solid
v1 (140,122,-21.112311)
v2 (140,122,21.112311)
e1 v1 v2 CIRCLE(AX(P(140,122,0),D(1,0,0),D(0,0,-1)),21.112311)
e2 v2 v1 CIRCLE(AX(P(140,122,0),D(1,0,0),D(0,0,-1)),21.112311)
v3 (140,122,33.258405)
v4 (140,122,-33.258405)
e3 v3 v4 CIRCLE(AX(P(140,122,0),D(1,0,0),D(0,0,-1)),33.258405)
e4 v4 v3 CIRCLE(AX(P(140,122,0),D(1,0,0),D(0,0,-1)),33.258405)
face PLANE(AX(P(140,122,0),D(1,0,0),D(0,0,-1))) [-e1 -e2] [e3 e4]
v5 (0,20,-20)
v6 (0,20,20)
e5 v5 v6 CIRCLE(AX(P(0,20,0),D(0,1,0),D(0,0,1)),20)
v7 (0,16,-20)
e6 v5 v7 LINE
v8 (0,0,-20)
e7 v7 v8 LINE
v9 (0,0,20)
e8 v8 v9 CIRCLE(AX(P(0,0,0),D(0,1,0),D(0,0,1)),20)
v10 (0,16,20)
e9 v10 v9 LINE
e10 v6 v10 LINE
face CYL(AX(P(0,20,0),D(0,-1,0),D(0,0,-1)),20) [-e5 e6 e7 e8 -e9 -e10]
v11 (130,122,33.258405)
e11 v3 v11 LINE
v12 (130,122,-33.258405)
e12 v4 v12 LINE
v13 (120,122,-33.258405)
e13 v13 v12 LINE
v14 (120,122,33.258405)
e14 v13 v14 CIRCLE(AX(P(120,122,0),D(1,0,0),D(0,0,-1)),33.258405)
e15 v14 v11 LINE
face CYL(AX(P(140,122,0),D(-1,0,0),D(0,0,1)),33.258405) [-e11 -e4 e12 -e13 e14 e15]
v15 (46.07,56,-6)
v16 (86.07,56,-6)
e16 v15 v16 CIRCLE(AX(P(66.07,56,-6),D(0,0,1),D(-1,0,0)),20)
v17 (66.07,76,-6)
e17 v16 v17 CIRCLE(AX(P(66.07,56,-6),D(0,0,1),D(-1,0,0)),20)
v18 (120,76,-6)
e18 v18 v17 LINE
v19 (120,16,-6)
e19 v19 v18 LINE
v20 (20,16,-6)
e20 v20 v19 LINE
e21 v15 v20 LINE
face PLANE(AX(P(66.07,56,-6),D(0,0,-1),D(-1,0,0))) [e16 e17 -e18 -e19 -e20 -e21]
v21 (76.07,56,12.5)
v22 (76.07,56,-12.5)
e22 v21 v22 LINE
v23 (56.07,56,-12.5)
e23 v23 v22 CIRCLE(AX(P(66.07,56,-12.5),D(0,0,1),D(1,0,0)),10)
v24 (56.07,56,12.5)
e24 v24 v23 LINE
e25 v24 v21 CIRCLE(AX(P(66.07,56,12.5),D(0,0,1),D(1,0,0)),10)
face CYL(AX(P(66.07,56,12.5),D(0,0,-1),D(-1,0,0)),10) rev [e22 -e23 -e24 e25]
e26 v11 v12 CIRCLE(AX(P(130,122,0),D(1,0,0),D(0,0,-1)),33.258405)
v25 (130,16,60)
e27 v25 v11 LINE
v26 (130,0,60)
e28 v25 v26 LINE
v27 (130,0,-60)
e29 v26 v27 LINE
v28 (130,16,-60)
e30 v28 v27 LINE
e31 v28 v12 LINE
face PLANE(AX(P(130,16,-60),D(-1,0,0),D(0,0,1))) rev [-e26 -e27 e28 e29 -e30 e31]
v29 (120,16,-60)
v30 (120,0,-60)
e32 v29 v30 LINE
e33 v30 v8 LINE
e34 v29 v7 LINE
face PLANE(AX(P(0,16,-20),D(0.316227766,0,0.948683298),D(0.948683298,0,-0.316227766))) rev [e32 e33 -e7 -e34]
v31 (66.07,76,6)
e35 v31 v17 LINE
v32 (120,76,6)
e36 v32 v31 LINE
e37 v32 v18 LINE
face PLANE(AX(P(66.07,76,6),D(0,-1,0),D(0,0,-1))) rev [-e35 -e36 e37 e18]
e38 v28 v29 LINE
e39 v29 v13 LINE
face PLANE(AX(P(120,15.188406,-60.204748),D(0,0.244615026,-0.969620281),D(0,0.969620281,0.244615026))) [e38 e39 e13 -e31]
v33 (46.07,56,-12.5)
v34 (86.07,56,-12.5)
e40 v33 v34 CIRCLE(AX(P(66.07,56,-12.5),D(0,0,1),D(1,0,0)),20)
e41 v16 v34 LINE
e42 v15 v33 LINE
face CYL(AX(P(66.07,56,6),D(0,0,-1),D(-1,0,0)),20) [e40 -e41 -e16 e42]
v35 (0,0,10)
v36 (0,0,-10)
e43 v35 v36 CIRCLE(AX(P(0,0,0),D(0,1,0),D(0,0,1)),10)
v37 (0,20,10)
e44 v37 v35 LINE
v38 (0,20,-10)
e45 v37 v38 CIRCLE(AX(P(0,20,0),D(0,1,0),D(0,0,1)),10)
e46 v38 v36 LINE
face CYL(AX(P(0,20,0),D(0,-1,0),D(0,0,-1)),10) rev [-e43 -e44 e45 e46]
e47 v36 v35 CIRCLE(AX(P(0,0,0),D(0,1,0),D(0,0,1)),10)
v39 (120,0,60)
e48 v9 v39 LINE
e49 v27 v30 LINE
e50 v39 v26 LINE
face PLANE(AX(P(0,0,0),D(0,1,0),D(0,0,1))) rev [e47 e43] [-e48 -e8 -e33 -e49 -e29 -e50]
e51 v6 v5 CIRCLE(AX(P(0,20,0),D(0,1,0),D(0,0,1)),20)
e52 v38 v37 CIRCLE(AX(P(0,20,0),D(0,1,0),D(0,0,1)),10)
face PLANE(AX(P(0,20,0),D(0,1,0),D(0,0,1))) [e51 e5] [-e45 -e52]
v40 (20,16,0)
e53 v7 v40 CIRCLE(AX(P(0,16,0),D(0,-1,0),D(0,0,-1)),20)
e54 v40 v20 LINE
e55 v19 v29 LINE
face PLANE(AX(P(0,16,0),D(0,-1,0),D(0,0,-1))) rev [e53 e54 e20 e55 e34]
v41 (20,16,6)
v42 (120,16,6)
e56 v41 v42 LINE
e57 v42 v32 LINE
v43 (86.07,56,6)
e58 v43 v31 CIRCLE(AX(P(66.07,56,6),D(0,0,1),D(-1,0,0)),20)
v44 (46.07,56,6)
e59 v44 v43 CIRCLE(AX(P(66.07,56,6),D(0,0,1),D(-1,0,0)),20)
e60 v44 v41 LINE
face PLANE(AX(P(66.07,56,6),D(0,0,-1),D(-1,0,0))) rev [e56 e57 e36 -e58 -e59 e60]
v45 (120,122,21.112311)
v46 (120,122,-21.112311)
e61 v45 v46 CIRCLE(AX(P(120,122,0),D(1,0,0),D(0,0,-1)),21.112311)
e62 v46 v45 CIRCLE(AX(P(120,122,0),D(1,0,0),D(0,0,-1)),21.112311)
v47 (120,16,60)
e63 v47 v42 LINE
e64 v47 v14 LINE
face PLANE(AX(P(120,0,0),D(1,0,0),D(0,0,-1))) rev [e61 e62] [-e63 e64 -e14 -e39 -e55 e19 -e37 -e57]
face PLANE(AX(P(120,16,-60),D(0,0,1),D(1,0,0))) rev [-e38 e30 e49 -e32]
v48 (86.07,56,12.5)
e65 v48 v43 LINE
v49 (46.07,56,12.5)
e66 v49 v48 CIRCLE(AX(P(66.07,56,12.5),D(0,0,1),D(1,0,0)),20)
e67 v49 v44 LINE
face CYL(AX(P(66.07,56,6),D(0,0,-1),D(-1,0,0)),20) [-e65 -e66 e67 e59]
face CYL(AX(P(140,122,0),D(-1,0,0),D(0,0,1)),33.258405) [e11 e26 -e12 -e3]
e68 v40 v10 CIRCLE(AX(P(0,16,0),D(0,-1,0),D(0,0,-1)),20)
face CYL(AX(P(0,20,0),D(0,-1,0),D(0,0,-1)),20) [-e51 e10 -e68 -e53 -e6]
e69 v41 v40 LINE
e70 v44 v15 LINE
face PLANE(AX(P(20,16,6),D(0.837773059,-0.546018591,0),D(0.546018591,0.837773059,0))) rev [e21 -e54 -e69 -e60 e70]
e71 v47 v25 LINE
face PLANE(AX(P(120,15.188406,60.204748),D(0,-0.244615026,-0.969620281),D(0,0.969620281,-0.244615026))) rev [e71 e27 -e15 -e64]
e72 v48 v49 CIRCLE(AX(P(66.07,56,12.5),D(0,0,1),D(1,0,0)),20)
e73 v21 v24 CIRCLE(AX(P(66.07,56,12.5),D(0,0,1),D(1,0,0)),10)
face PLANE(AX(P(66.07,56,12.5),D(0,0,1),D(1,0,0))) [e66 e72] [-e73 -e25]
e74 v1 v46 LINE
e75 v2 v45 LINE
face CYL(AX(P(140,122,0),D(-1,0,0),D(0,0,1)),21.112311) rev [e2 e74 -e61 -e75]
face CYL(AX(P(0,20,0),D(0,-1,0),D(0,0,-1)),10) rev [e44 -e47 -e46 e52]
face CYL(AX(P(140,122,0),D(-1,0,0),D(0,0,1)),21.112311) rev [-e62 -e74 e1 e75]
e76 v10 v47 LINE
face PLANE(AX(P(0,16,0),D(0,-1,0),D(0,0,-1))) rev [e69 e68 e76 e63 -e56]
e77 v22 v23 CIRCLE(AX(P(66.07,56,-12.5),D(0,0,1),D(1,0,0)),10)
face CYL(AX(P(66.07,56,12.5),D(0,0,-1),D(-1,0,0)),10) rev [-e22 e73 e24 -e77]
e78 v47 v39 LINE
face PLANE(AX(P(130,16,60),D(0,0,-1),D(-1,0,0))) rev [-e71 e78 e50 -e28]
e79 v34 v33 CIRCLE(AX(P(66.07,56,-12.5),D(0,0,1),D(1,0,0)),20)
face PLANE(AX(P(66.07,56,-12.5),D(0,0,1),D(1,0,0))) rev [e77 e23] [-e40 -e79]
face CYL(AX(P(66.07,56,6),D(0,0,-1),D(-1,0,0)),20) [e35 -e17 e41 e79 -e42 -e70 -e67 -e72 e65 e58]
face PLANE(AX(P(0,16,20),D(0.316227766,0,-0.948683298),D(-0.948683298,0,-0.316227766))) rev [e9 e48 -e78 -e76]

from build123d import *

# Parameters (mm, degrees)
BASE_BOSS_RING_SKETCH_R    = 20
BASE_BOSS_RING_SKETCH_R_2  = 10
BASE_BOSS_RING_40_DEPTH    = 20
BASE_PLATE_DEPTH           = 16
UPPER_BOSS_RING_SKETCH_R   = 33.258405
UPPER_BOSS_RING_SKETCH_R_2 = 21.112311
UPPER_BOSS_RING_DEPTH      = 10
UPRIGHT_WEB_DEPTH          = 10
MIDDLE_BOSS_SKETCH_R       = 20
MIDDLE_BOSS_SKETCH_R_2     = 10
MIDDLE_BOSS_DEPTH          = 12.5
GUSSET_RIB_DEPTH           = 6
MIDDLE_BOSS_BORE_SKETCH_R  = 10
MIDDLE_BOSS_BORE_DEPTH     = 220.228585


with BuildPart() as part:
    # Base Boss Ring Sketch → Base Boss Ring Ø40 (new body)
    with BuildSketch(Plane(origin=(0, 0, 0), x_dir=(1, 0, 0), z_dir=(0, 1, 0))):
        with Locations(Location((0, 0, 0), (0, 0, 270))):
            Circle(BASE_BOSS_RING_SKETCH_R)
        with Locations(Location((0, 0, 0), (0, 0, 270))):
            Circle(BASE_BOSS_RING_SKETCH_R_2, mode=Mode.SUBTRACT)
    extrude(amount=BASE_BOSS_RING_40_DEPTH)

    # Base Plate Sketch → Base Plate (add)
    with BuildSketch(Plane(origin=(0, 0, 0), x_dir=(1, 0, 0), z_dir=(0, 1, 0))):
        with BuildLine():
            Line((120, 60), (130, 60))
            Line((130, 60), (130, -60))
            Line((130, -60), (120, -60))
            Line((120, -60), (0, -20))
            ThreePointArc((0, -20), (20, 0), (0, 20))
            Line((0, 20), (120, 60))
        make_face()
    extrude(amount=BASE_PLATE_DEPTH)



with BuildPart() as body_2:
    # Upper Boss Ring Sketch → Upper Boss Ring (new, symmetric)
    with BuildSketch(Plane(origin=(130, 0, 0), x_dir=(0, 0, -1), z_dir=(1, 0, 0))):
        with Locations((0, 122)):
            Circle(UPPER_BOSS_RING_SKETCH_R)
        with Locations((0, 122)):
            Circle(UPPER_BOSS_RING_SKETCH_R_2, mode=Mode.SUBTRACT)
    extrude(amount=UPPER_BOSS_RING_DEPTH, both=True)


with BuildPart() as part_1:
    add(part.part)

    add(body_2.part)  # Upright Web merges body 2
    # Upright Web Sketch → Upright Web (add)
    with BuildSketch(Plane(origin=(130, 0, 0), x_dir=(0, 0, -1), z_dir=(1, 0, 0))):
        with BuildLine():
            ThreePointArc((-33.258405, 122), (0, 88.741595), (33.258405, 122))
            Line((33.258405, 122), (60, 16))
            Line((60, 16), (-60, 16))
            Line((-60, 16), (-33.258405, 122))
        make_face()
    extrude(amount=-UPRIGHT_WEB_DEPTH)



with BuildPart() as body_2_2:
    # Middle Boss Sketch → Middle Boss (new, symmetric)
    with BuildSketch(Plane.XY):
        with Locations((66.07, 56)):
            Circle(MIDDLE_BOSS_SKETCH_R)
        with Locations((66.07, 56)):
            Circle(MIDDLE_BOSS_SKETCH_R_2, mode=Mode.SUBTRACT)
    extrude(amount=MIDDLE_BOSS_DEPTH, both=True)


with BuildPart() as part_2:
    add(part_1.part)

    add(body_2_2.part)  # Gusset Rib merges body 2 2
    # Gusset Rib Sketch → Gusset Rib (add, symmetric)
    with BuildSketch(Plane.XY):
        with BuildLine():
            Line((66.07, 76), (120, 76))
            Line((120, 76), (120, 16))
            Line((120, 16), (20, 16))
            Line((20, 16), (46.07, 56))
            ThreePointArc((46.07, 56), (51.927864, 70.142136), (66.07, 76))
        make_face()
    extrude(amount=GUSSET_RIB_DEPTH, both=True)

    # Middle Boss Bore Sketch → Middle Boss Bore (cut, through all)
    with BuildSketch(Plane.XY.offset(6)):
        with Locations((66.07, 56)):
            Circle(MIDDLE_BOSS_BORE_SKETCH_R)
    extrude(amount=-MIDDLE_BOSS_BORE_DEPTH, mode=Mode.SUBTRACT)


solid = part_2.part
